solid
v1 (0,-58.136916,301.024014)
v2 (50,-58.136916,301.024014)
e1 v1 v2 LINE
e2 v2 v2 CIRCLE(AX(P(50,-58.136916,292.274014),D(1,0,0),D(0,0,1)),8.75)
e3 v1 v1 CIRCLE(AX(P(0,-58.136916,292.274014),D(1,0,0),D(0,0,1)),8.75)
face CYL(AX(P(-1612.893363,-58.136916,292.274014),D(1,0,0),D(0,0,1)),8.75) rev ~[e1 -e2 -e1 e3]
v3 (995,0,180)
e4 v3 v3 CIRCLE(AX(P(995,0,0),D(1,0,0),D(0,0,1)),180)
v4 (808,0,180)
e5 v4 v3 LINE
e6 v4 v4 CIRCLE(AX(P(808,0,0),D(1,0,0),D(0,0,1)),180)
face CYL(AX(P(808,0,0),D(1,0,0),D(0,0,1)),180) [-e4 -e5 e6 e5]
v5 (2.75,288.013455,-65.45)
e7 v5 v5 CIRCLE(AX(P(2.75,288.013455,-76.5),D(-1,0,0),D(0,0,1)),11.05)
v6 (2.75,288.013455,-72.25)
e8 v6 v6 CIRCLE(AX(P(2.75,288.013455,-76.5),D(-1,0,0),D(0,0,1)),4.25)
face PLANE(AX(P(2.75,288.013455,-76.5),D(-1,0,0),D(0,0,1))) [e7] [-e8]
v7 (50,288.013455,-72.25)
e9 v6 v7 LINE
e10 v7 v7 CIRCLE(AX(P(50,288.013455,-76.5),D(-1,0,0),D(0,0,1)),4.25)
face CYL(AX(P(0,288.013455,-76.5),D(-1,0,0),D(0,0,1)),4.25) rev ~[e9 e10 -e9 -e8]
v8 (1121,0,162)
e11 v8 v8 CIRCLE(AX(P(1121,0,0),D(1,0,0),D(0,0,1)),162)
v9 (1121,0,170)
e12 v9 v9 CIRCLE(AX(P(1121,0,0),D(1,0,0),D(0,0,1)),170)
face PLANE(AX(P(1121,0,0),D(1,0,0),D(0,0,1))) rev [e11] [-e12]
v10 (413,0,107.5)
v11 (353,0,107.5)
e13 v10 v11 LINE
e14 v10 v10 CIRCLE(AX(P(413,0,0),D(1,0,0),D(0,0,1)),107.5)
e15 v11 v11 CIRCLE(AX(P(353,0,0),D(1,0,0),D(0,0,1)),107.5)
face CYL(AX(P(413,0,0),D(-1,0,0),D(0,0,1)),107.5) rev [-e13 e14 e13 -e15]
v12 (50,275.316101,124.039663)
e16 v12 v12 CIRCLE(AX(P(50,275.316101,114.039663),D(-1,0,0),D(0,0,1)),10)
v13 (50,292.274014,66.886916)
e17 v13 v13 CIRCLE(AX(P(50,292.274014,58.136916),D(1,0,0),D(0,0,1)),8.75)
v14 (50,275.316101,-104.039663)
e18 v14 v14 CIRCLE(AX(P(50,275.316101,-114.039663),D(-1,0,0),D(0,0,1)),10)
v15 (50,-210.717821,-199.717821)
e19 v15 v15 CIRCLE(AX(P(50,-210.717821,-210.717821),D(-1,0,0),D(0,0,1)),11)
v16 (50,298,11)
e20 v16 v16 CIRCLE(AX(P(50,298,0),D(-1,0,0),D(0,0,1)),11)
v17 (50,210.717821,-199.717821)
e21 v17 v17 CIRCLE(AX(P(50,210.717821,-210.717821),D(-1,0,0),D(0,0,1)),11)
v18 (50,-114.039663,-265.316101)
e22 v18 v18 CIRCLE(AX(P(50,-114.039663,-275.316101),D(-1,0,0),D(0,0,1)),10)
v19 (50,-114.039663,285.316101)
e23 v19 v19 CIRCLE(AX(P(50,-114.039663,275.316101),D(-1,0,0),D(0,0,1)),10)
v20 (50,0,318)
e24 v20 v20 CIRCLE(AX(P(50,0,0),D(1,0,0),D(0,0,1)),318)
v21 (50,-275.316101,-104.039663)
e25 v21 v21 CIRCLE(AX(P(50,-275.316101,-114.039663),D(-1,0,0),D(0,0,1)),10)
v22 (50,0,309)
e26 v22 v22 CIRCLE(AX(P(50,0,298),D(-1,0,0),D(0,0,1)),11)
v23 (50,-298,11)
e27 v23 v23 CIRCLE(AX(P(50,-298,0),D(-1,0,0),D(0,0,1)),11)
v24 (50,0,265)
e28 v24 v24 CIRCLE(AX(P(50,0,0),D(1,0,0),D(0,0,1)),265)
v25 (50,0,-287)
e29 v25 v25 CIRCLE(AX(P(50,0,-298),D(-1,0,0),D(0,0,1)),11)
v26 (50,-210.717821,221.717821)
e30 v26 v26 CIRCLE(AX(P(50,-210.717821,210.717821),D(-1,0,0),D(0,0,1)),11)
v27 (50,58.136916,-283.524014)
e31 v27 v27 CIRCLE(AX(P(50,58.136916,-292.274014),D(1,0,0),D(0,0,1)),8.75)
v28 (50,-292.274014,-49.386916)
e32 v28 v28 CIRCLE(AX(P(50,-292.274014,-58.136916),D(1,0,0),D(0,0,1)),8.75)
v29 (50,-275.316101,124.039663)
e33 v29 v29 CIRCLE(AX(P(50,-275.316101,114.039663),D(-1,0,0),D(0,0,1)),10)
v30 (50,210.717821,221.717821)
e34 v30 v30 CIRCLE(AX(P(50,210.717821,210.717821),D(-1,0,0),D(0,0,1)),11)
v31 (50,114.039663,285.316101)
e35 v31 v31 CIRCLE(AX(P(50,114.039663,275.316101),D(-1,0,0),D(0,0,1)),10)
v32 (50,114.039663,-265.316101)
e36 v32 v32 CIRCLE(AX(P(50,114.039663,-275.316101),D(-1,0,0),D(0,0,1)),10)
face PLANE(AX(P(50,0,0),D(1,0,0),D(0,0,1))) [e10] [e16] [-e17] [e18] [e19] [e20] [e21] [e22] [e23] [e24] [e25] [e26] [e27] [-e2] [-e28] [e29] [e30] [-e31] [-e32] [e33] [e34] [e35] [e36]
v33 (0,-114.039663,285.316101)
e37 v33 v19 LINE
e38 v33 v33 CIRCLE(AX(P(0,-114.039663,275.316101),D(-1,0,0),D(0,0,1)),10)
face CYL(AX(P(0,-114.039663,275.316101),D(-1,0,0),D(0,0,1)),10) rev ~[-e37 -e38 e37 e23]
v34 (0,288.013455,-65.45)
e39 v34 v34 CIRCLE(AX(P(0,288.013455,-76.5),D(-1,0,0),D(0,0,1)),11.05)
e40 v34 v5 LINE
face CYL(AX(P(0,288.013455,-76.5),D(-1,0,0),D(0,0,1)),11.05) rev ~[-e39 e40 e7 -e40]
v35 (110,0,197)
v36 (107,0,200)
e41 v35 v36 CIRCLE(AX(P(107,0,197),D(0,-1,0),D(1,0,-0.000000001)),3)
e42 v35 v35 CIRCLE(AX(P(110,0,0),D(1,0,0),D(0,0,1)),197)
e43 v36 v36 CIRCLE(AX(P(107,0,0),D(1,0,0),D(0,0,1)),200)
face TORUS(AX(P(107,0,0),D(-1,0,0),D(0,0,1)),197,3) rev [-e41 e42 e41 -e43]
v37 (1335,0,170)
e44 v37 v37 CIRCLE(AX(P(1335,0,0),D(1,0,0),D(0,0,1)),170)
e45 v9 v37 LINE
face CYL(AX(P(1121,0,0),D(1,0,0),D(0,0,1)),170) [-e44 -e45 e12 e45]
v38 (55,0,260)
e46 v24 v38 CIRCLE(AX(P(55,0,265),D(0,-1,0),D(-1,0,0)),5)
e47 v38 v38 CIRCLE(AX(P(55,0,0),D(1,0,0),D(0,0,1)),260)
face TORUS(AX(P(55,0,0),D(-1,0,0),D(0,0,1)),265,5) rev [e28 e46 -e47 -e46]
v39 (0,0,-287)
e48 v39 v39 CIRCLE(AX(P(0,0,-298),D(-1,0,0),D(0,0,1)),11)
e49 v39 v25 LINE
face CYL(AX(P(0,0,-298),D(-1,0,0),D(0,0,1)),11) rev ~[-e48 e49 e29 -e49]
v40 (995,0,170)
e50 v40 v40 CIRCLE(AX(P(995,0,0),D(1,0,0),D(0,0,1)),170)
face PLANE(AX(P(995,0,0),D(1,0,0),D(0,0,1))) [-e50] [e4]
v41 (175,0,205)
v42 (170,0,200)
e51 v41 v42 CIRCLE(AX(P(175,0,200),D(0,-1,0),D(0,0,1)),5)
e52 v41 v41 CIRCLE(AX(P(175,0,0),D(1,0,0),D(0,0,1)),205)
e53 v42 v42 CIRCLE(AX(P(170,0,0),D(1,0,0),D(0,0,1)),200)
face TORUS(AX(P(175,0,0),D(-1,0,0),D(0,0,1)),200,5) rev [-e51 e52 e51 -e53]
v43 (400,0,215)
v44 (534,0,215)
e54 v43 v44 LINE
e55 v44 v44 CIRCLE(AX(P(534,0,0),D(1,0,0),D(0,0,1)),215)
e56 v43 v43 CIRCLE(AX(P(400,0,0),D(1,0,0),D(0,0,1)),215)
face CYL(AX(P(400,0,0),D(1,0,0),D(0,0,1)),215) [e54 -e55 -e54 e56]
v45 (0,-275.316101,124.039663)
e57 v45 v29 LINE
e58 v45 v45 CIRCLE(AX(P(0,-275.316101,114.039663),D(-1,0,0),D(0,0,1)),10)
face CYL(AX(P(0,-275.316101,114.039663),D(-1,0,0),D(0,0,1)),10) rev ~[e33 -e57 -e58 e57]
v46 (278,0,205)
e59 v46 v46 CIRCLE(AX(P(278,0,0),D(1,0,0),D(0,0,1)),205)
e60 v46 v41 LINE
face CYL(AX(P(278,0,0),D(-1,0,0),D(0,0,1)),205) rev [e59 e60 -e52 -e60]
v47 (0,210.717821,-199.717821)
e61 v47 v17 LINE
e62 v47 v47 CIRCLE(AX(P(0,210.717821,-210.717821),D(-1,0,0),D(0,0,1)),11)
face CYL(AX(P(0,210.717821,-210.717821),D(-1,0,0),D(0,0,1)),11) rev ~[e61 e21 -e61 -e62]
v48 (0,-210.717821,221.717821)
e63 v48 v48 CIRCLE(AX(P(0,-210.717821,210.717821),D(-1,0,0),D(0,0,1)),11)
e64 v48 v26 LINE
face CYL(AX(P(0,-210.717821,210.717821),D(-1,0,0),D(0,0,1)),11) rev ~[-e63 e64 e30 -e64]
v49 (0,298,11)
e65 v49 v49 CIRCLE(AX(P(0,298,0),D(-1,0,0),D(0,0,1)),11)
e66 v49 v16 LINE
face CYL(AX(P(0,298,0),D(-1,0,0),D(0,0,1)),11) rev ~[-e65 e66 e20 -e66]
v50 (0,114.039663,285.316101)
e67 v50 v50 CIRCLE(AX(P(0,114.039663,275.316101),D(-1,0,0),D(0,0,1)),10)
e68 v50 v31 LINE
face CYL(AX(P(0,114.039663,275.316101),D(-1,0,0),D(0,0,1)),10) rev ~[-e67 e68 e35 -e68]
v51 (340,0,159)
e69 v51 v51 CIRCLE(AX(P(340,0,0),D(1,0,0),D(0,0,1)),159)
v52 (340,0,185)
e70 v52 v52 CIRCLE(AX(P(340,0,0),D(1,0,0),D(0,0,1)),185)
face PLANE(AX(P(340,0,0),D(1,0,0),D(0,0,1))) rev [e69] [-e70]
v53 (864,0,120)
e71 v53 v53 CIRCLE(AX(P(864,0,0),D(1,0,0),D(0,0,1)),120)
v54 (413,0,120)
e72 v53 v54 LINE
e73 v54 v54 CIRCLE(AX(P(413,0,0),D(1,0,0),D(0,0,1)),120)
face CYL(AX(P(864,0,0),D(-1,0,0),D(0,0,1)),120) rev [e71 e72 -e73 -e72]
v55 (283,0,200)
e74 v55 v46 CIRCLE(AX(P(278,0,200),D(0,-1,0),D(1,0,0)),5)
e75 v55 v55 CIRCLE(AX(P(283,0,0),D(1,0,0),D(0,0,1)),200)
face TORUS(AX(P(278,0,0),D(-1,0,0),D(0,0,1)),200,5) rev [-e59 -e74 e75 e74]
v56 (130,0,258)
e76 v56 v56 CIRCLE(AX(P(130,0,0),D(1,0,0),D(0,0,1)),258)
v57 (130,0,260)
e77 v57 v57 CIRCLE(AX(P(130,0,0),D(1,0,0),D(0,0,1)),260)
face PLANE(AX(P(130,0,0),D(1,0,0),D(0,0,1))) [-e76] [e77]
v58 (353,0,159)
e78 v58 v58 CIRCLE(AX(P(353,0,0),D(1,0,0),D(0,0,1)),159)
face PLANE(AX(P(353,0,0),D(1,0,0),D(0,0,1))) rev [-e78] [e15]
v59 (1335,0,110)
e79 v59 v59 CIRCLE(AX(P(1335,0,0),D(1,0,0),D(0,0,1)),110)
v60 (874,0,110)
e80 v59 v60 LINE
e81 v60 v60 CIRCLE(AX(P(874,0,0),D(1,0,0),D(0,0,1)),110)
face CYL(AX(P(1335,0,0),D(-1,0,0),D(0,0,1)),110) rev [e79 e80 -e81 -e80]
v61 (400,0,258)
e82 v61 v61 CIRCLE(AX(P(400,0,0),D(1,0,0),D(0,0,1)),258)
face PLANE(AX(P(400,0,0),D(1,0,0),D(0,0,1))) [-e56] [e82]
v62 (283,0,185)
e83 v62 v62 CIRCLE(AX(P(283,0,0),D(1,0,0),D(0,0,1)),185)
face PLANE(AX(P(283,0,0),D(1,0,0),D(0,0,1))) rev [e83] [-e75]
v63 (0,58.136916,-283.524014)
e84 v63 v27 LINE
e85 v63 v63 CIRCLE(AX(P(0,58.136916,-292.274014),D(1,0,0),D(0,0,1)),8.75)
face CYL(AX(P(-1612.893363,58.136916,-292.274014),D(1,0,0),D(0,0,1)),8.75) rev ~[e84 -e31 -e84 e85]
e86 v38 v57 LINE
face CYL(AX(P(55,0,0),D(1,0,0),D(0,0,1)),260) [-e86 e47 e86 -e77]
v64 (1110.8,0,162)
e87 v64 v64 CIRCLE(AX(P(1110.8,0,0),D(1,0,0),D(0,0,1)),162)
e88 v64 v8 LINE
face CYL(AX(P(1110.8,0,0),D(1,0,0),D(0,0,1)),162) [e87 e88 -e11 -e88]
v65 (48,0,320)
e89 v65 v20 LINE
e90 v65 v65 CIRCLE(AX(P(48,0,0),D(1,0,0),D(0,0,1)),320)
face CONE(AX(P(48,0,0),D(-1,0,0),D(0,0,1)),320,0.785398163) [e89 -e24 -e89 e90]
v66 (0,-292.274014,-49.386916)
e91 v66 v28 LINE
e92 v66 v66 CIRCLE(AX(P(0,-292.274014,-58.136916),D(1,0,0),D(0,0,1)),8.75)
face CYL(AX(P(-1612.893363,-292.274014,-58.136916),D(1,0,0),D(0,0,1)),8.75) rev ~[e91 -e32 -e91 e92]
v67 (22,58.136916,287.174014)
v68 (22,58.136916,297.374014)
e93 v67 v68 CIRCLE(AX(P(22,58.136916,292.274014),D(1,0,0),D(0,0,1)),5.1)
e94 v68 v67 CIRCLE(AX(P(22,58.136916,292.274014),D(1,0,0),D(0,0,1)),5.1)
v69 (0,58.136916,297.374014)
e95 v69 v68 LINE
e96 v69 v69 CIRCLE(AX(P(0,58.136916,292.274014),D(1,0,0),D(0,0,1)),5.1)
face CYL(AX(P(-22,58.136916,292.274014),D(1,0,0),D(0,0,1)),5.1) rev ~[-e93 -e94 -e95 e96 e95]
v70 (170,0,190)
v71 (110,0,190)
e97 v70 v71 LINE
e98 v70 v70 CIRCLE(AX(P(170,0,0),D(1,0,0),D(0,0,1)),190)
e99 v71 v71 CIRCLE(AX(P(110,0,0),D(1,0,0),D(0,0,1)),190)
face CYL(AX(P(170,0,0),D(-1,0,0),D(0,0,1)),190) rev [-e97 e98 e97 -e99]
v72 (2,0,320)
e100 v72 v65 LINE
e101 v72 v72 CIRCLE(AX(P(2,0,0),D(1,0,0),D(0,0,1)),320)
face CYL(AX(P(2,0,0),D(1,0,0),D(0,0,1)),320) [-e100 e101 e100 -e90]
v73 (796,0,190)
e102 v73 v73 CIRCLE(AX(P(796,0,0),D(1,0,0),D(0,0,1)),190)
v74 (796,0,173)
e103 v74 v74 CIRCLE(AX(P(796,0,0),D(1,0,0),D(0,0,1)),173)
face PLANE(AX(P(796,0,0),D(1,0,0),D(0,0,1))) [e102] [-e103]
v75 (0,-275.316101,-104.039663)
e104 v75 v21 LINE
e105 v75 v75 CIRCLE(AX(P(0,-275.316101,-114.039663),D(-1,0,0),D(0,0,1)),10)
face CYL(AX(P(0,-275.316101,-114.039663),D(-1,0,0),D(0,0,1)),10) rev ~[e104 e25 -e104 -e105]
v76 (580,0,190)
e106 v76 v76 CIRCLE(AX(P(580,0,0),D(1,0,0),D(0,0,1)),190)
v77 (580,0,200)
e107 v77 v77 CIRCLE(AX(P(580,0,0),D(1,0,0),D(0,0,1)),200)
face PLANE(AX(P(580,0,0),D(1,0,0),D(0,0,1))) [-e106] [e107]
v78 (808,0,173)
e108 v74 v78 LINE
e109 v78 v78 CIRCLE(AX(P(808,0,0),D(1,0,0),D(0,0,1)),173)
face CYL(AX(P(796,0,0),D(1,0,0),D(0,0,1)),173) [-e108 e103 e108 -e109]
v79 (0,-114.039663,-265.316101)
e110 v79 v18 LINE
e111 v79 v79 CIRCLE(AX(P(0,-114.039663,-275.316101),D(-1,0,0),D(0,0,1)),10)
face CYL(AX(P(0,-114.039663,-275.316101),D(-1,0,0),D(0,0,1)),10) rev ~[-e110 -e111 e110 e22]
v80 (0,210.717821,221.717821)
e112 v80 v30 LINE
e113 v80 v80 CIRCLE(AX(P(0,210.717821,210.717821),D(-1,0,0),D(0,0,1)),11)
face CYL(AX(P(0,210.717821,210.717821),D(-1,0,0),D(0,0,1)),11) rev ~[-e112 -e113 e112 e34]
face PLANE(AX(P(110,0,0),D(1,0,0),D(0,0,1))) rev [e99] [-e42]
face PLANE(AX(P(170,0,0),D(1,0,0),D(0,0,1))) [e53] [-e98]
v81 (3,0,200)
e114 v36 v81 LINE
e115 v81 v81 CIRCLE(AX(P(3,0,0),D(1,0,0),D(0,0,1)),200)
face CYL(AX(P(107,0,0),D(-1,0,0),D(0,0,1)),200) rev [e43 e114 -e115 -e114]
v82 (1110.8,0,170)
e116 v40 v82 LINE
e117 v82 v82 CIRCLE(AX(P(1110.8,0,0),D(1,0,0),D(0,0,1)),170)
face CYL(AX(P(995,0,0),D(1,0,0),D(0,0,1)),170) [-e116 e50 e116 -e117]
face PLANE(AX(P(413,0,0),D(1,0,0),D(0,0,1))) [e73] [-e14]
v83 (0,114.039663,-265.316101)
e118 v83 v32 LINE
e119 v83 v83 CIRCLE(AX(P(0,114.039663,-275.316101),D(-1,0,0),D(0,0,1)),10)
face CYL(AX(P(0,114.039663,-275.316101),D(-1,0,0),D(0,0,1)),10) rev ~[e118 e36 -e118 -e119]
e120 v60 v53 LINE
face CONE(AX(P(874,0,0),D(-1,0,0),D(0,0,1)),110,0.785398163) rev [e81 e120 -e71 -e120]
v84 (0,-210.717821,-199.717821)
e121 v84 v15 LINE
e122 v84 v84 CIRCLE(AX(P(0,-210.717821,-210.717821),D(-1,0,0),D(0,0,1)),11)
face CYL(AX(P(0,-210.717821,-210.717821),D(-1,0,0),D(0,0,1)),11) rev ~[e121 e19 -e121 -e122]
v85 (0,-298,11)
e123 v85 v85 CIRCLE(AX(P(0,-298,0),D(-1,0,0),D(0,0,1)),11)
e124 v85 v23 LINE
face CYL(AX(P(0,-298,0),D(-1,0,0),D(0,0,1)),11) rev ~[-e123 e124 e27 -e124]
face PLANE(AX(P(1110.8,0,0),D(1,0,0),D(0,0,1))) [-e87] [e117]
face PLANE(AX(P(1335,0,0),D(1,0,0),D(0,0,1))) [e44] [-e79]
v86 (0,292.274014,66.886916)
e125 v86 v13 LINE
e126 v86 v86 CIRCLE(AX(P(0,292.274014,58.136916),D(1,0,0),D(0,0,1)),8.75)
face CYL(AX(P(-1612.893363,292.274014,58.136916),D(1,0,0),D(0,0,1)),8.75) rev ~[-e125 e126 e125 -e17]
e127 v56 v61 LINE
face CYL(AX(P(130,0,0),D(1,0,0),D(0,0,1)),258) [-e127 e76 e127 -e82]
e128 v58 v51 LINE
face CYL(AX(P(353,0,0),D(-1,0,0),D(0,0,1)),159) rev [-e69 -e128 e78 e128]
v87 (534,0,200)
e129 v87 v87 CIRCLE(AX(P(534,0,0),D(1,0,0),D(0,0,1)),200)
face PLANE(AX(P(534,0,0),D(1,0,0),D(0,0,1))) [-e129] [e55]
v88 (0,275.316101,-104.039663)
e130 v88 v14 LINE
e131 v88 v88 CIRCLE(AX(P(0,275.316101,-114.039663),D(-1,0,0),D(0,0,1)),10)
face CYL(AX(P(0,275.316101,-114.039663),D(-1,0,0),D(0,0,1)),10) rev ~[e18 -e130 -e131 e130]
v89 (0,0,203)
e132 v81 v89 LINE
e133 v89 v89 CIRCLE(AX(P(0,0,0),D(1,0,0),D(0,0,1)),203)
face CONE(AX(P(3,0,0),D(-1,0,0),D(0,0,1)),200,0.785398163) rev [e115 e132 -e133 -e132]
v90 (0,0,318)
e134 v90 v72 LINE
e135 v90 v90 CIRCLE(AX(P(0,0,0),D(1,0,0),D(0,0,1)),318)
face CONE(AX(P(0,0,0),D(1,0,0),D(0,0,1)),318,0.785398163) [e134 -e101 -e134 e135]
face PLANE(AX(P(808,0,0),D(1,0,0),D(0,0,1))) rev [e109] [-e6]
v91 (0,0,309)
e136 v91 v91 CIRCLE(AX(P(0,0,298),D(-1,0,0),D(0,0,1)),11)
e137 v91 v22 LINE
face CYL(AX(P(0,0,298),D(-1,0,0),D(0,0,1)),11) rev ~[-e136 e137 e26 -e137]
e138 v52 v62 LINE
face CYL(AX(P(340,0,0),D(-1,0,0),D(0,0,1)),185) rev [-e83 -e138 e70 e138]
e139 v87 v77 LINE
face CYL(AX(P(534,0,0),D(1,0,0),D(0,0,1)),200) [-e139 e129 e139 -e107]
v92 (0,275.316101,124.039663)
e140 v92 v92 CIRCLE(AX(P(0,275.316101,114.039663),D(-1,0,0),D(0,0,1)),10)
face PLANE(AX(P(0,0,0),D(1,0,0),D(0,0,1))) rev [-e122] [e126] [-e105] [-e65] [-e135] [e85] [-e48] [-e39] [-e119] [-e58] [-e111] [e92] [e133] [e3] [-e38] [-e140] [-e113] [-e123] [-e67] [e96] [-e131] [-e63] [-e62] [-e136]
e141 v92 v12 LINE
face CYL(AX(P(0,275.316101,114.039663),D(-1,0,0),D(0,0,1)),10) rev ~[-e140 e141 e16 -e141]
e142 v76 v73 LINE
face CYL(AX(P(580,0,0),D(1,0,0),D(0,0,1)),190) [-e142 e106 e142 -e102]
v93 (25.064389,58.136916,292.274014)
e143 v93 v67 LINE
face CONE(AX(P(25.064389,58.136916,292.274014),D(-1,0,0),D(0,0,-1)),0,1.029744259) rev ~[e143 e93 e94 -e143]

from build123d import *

# Parameters (mm, degrees)
M12_TAPPED_HOLE1_D     = 10.2
M12_TAPPED_HOLE1_DEPTH = 22
M12_TAPPED_HOLE1_TIP   = 3.064389157
M20_TAPPED_HOLE1_D     = 17.5
SKETCH3_R              = 10
SKETCH3_R_2            = 11
SKETCH3_R_3            = 4.25
CUT_EXTRUDE2_DEPTH     = 1410.618742781
SKETCH7_R              = 11.05
CUT_EXTRUDE3_DEPTH     = 2.75


with BuildPart() as part:
    # Sketch1 → Revolve1 (revolve)
    with BuildSketch(Plane.XY, mode=Mode.PRIVATE) as revolve1_sk:
        with BuildLine():
            Line((0, 203), (0, 318))
            Line((0, 318), (2, 320))
            Line((2, 320), (48, 320))
            Line((48, 320), (50, 318))
            Line((50, 318), (50, 265))
            ThreePointArc((50, 265), (51.464466094, 261.464466094), (55, 260))
            Line((55, 260), (130, 260))
            Line((130, 260), (130, 258))
            Line((130, 258), (400, 258))
            Line((400, 258), (400, 215))
            Line((400, 215), (534, 215))
            Line((534, 215), (534, 200))
            Line((534, 200), (580, 200))
            Line((580, 200), (580, 190))
            Line((580, 190), (796, 190))
            Line((796, 190), (796, 173))
            Line((796, 173), (808, 173))
            Line((808, 173), (808, 180))
            Line((808, 180), (995, 180))
            Line((995, 180), (995, 170))
            Line((995, 170), (1110.8, 170))
            Line((1110.8, 170), (1110.8, 162))
            Line((1110.8, 162), (1121, 162))
            Line((1121, 162), (1121, 170))
            Line((1121, 170), (1335, 170))
            Line((1335, 170), (1335, 110))
            Line((1335, 110), (874, 110))
            Line((874, 110), (864, 120))
            Line((864, 120), (413, 120))
            Line((413, 120), (413, 107.5))
            Line((413, 107.5), (353, 107.5))
            Line((353, 107.5), (353, 159))
            Line((353, 159), (340, 159))
            Line((340, 159), (340, 185))
            Line((340, 185), (283, 185))
            Line((283, 185), (283, 200))
            ThreePointArc((283, 200), (281.535533906, 203.535533906), (278, 205))
            Line((278, 205), (175, 205))
            ThreePointArc((175, 205), (171.464466094, 203.535533906), (170, 200))
            Line((170, 200), (170, 190))
            Line((170, 190), (110, 190))
            Line((110, 190), (110, 197))
            ThreePointArc((110, 197), (109.121320344, 199.121320344), (107, 200))
            Line((107, 200), (3, 200))
            Line((3, 200), (0, 203))
        make_face()
    revolve(revolve1_sk.sketch.rotate(Axis((0, 0, 0), (1, 0, 0)), 90), axis=Axis((0, 0, 0), (1, 0, 0)))

    # M12 Tapped Hole1
    with Locations(Plane(origin=(0, 58.136915961, 292.27401356), x_dir=(0, 0, -1), z_dir=(-1, 0, 0))):
        with Locations((0, 0)):
            Hole(M12_TAPPED_HOLE1_D / 2, depth=M12_TAPPED_HOLE1_DEPTH)
            with Locations((0, 0, -(M12_TAPPED_HOLE1_DEPTH + M12_TAPPED_HOLE1_TIP / 2))):  # 118° drill point
                Cone(0, M12_TAPPED_HOLE1_D / 2, M12_TAPPED_HOLE1_TIP, mode=Mode.SUBTRACT)

    # M20 Tapped Hole1 (through all)
    with Locations(Plane(origin=(0, 292.27401356, 58.136915961), x_dir=(0, 0, -1), z_dir=(-1, 0, 0))):
        with Locations((0, 0), (350.410929521, 234.137097599), (116.273831922, 584.54802712), (-234.137097599, 350.410929521)):
            Hole(M20_TAPPED_HOLE1_D / 2)

    # Sketch3 → Cut-Extrude2 (cut, through all)
    with BuildSketch(Plane.ZY):
        with Locations((114.039662845, 275.316100688)):
            Circle(SKETCH3_R)
        with Locations((0, 298)):
            Circle(SKETCH3_R_2)
        with Locations((210.717820794, 210.717820794)):
            Circle(SKETCH3_R_2)
        with Locations((275.316100688, 114.039662845)):
            Circle(SKETCH3_R)
        with Locations((298, 0)):
            Circle(SKETCH3_R_2)
        with Locations((275.316100688, -114.039662845)):
            Circle(SKETCH3_R)
        with Locations((210.717820794, -210.717820794)):
            Circle(SKETCH3_R_2)
        with Locations((114.039662845, -275.316100688)):
            Circle(SKETCH3_R)
        with Locations((0, -298)):
            Circle(SKETCH3_R_2)
        with Locations((-114.039662845, -275.316100688)):
            Circle(SKETCH3_R)
        with Locations((-210.717820794, -210.717820794)):
            Circle(SKETCH3_R_2)
        with Locations((-275.316100688, -114.039662845)):
            Circle(SKETCH3_R)
        with Locations((-298, 0)):
            Circle(SKETCH3_R_2)
        with Locations((-275.316100688, 114.039662845)):
            Circle(SKETCH3_R)
        with Locations((-210.717820794, 210.717820794)):
            Circle(SKETCH3_R_2)
        with Locations((-114.039662845, 275.316100688)):
            Circle(SKETCH3_R)
        with Locations((-76.5, 288.013454547)):
            Circle(SKETCH3_R_3)
    extrude(amount=-CUT_EXTRUDE2_DEPTH, mode=Mode.SUBTRACT)

    # Sketch7 → Cut-Extrude3 (cut)
    with BuildSketch(Plane.ZY):
        with Locations((-76.5, 288.013454547)):
            Circle(SKETCH7_R)
    extrude(amount=-CUT_EXTRUDE3_DEPTH, mode=Mode.SUBTRACT)


solid = part.part
